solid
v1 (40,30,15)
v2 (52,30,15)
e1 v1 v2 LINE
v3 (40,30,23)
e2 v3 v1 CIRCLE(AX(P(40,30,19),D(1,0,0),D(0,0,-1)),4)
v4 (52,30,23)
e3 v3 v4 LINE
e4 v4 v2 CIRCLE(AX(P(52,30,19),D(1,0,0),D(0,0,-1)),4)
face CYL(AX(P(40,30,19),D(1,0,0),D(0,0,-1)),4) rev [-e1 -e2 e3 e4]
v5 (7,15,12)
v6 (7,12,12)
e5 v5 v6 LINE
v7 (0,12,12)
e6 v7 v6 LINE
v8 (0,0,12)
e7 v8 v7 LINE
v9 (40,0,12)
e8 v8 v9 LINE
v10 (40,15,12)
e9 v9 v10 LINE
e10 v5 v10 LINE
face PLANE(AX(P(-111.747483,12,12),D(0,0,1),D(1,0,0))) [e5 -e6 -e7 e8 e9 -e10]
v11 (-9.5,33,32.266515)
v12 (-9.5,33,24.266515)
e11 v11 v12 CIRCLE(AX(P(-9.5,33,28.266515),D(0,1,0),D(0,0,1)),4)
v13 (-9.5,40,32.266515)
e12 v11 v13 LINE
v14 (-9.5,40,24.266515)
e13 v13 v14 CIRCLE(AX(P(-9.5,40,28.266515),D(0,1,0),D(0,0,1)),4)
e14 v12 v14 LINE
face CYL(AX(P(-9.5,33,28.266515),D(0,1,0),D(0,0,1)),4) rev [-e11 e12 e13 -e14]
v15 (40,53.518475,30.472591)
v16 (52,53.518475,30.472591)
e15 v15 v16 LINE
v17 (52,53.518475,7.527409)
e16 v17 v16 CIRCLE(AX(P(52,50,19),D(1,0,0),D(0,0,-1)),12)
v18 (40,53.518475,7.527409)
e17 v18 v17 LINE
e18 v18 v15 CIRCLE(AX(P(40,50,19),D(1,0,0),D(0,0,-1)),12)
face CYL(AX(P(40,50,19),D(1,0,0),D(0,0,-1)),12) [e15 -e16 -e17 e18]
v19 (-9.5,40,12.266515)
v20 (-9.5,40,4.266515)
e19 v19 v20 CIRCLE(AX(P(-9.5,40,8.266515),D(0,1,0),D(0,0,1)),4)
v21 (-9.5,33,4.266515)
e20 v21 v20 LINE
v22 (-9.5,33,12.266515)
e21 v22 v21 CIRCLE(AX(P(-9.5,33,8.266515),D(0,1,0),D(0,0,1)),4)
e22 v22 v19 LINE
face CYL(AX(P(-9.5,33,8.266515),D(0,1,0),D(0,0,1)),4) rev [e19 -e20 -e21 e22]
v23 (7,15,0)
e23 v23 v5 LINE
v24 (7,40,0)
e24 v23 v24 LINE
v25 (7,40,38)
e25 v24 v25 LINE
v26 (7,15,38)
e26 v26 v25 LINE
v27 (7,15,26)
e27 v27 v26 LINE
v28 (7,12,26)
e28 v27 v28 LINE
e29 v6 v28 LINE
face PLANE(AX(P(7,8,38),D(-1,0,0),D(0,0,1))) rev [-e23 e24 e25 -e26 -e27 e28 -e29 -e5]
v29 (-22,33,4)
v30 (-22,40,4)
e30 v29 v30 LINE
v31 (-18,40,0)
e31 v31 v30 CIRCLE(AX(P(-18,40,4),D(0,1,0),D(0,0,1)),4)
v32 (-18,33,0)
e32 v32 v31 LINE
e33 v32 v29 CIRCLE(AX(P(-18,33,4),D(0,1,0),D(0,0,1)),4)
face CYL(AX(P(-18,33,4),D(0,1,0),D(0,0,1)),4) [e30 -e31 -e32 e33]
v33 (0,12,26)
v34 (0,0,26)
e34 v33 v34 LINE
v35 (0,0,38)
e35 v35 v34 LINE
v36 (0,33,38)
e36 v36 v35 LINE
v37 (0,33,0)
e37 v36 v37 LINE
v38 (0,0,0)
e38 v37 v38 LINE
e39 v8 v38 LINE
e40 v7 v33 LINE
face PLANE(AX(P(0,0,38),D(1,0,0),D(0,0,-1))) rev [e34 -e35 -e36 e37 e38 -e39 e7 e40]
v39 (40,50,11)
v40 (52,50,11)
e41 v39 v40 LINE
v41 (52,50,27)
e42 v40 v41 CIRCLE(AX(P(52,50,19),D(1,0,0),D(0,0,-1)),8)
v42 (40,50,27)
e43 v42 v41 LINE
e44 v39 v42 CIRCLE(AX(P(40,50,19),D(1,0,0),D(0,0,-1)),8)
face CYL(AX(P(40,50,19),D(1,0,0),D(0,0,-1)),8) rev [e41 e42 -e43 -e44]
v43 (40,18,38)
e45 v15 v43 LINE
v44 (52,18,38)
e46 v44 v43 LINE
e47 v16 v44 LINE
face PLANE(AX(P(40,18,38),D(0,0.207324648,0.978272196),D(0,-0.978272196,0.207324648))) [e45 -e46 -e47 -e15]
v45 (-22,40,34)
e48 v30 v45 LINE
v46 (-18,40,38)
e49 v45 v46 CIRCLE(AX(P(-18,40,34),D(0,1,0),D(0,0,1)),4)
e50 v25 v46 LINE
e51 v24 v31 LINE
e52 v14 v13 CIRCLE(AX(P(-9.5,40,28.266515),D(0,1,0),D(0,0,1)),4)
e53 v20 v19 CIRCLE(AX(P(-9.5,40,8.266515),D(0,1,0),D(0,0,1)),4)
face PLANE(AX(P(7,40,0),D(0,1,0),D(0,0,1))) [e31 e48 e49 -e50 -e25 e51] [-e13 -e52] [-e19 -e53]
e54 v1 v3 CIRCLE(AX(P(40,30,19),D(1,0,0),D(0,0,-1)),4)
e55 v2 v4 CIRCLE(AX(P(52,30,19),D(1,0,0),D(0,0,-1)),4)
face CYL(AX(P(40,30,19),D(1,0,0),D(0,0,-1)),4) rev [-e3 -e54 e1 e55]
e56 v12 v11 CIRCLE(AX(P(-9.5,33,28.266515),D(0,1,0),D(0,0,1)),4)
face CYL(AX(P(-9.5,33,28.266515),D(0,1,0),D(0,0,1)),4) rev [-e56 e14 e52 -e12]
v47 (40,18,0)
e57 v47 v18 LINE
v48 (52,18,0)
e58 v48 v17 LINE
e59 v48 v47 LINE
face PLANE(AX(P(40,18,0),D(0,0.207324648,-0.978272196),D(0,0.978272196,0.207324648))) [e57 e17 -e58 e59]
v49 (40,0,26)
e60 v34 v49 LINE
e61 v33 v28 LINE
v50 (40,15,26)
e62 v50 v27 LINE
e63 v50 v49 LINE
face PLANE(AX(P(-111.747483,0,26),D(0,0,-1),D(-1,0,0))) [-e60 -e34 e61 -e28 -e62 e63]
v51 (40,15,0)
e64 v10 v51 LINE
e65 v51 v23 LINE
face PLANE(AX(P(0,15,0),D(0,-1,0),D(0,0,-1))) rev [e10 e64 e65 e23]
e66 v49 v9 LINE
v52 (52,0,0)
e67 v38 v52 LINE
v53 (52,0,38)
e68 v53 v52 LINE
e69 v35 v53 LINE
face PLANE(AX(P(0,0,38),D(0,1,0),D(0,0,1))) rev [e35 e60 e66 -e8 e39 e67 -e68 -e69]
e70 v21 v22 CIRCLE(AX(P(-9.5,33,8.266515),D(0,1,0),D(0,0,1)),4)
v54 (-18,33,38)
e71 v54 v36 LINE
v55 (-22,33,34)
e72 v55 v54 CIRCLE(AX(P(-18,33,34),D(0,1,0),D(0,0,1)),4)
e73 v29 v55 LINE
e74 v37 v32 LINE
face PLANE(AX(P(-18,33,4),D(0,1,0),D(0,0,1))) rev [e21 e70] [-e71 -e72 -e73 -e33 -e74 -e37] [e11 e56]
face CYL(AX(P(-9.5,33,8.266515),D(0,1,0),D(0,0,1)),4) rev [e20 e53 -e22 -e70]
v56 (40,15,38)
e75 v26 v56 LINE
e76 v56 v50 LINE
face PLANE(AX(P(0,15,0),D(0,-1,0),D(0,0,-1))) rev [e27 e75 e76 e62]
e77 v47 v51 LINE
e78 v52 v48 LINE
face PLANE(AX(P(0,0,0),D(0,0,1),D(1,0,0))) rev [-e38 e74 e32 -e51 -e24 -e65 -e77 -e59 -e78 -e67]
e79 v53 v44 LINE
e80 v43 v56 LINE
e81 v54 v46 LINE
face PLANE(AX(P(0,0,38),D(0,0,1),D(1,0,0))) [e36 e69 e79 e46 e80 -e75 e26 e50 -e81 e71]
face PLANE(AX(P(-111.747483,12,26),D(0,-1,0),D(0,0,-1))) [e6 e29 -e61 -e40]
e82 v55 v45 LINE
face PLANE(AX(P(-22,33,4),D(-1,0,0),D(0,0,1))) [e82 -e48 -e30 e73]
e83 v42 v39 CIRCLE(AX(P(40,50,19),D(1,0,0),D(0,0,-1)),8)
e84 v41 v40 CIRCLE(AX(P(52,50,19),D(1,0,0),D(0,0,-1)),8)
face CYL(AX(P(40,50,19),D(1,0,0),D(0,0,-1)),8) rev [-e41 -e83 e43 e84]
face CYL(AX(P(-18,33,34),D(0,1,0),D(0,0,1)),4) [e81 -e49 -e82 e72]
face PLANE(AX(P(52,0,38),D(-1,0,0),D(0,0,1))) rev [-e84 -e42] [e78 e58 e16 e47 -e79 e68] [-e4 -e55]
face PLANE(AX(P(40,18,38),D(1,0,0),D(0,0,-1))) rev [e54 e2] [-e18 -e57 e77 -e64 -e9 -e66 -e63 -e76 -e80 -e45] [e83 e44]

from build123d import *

# Parameters (mm, degrees)
BASE_BODY_DEPTH            = 38
UPRIGHT_LUG_DEPTH          = 12
CENTRE_SLOT_CUT_DEPTH      = 90.397986555
CENTRE_SLOT_CUT_DEPTH_BACK = 40
SIDE_WALL_SKETCH_W         = 7
SIDE_WALL_SKETCH_H         = 22
SIDE_WALL_DEPTH            = 38
TOP_FLANGE_DEPTH           = 7
SLOT_STEP_PAD_A_SKETCH_W   = 33
SLOT_STEP_PAD_A_SKETCH_H   = 12
SLOT_STEP_PAD_A_DEPTH      = 2
SLOT_STEP_PAD_B_SKETCH_W   = 33
SLOT_STEP_PAD_B_SKETCH_H   = 12
SLOT_STEP_PAD_B_DEPTH      = 2
FLANGE_HOLES_SKETCH_R      = 4
FLANGE_HOLES_2X_8_DEPTH    = 7
LUG_BORE_SKETCH_R          = 8
LUG_BORE_16_DEPTH          = 12
LUG_HOLE_SKETCH_R          = 4
LUG_HOLE_8_DEPTH           = 12
SLOT_STEP_BLOCK_A_SKETCH_W = 33
SLOT_STEP_BLOCK_A_SKETCH_H = 12
SLOT_STEP_BLOCK_A_DEPTH    = 5
SLOT_STEP_BLOCK_B_SKETCH_W = 33
SLOT_STEP_BLOCK_B_SKETCH_H = 12
SLOT_STEP_BLOCK_B_DEPTH    = 5


with BuildPart() as part:
    # Base Profile Sketch → Base Body (new body)
    with BuildSketch(Plane.XY):
        Polygon((0, 0), (52, 0), (52, 18), (40, 18), (40, 8), (12, 8), (7, 8), (7, 18), (0, 18), align=None)
    extrude(amount=BASE_BODY_DEPTH)

    # Upright Lug Sketch → Upright Lug (add)
    with BuildSketch(Plane(origin=(52, 0, 0), x_dir=(0, 0, -1), z_dir=(1, 0, 0))):
        with BuildLine():
            Line((-38, 18), (0, 18))
            Line((0, 18), (-7.527409318, 53.518474532))
            ThreePointArc((-7.527409318, 53.518474532), (-19, 62), (-30.472590682, 53.518474532))
            Line((-30.472590682, 53.518474532), (-38, 18))
        make_face()
    extrude(amount=-UPRIGHT_LUG_DEPTH)

    # Centre Slot Sketch → Centre Slot Cut (cut, two sides: drawn at the far end of the back side and taken through both)
    with BuildSketch(Plane.ZY.offset(-CENTRE_SLOT_CUT_DEPTH_BACK)):
        Polygon((26, -144.461890512), (26, 0), (26, 12), (12, 12), (12, 0), (12, -144.461890512), (12, -433.385671535), (26, -433.385671535), align=None)
    extrude(amount=CENTRE_SLOT_CUT_DEPTH + CENTRE_SLOT_CUT_DEPTH_BACK, mode=Mode.SUBTRACT)

    # Side Wall Sketch → Side Wall (add)
    with BuildSketch(Plane.XY.offset(38)):
        with Locations((3.5, 29)):
            Rectangle(SIDE_WALL_SKETCH_W, SIDE_WALL_SKETCH_H)
    extrude(amount=-SIDE_WALL_DEPTH)

    # Top Flange Sketch → Top Flange (add)
    with BuildSketch(Plane(origin=(0, 40, 0), x_dir=(1, 0, 0), z_dir=(0, 1, 0))):
        with BuildLine():
            Line((0, 0), (-18, 0))
            ThreePointArc((-18, 0), (-20.828427125, -1.171572875), (-22, -4))
            Line((-22, -4), (-22, -34))
            ThreePointArc((-22, -34), (-20.828427125, -36.828427125), (-18, -38))
            Line((-18, -38), (0, -38))
            Line((0, -38), (0, 0))
        make_face()
    extrude(amount=-TOP_FLANGE_DEPTH)

    # Slot Step Pad A Sketch → Slot Step Pad A (add)
    with BuildSketch(Plane(origin=(0, 8, 0), x_dir=(1, 0, 0), z_dir=(0, 1, 0))):
        with Locations((23.5, -32)):
            Rectangle(SLOT_STEP_PAD_A_SKETCH_W, SLOT_STEP_PAD_A_SKETCH_H)
    extrude(amount=SLOT_STEP_PAD_A_DEPTH)

    # Slot Step Pad B Sketch → Slot Step Pad B (add)
    with BuildSketch(Plane(origin=(0, 8, 0), x_dir=(1, 0, 0), z_dir=(0, 1, 0))):
        with Locations((23.5, -6)):
            Rectangle(SLOT_STEP_PAD_B_SKETCH_W, SLOT_STEP_PAD_B_SKETCH_H)
    extrude(amount=SLOT_STEP_PAD_B_DEPTH)

    # Flange Holes Sketch → Flange Holes 2xØ8 (cut)
    with BuildSketch(Plane(origin=(0, 40, 0), x_dir=(1, 0, 0), z_dir=(0, 1, 0))):
        with Locations(Location((-9.5, -8.266515029, 0), (0, 0, 270))):
            Circle(FLANGE_HOLES_SKETCH_R)
        with Locations(Location((-9.5, -28.266515029, 0), (0, 0, 270))):
            Circle(FLANGE_HOLES_SKETCH_R)
    extrude(amount=-FLANGE_HOLES_2X_8_DEPTH, mode=Mode.SUBTRACT)

    # Lug Bore Sketch → Lug Bore Ø16 (cut)
    with BuildSketch(Plane(origin=(52, 0, 0), x_dir=(0, 0, -1), z_dir=(1, 0, 0))):
        with Locations((-19, 50)):
            Circle(LUG_BORE_SKETCH_R)
    extrude(amount=-LUG_BORE_16_DEPTH, mode=Mode.SUBTRACT)

    # Lug Hole Sketch → Lug Hole Ø8 (cut)
    with BuildSketch(Plane(origin=(52, 0, 0), x_dir=(0, 0, -1), z_dir=(1, 0, 0))):
        with Locations((-19, 30)):
            Circle(LUG_HOLE_SKETCH_R)
    extrude(amount=-LUG_HOLE_8_DEPTH, mode=Mode.SUBTRACT)

    # Slot Step Block A Sketch → Slot Step Block A (add)
    with BuildSketch(Plane(origin=(0, 10, 0), x_dir=(1, 0, 0), z_dir=(0, 1, 0))):
        with Locations((23.5, -32)):
            Rectangle(SLOT_STEP_BLOCK_A_SKETCH_W, SLOT_STEP_BLOCK_A_SKETCH_H)
    extrude(amount=SLOT_STEP_BLOCK_A_DEPTH)

    # Slot Step Block B Sketch → Slot Step Block B (add)
    with BuildSketch(Plane(origin=(0, 10, 0), x_dir=(1, 0, 0), z_dir=(0, 1, 0))):
        with Locations((23.5, -6)):
            Rectangle(SLOT_STEP_BLOCK_B_SKETCH_W, SLOT_STEP_BLOCK_B_SKETCH_H)
    extrude(amount=SLOT_STEP_BLOCK_B_DEPTH)


solid = part.part
